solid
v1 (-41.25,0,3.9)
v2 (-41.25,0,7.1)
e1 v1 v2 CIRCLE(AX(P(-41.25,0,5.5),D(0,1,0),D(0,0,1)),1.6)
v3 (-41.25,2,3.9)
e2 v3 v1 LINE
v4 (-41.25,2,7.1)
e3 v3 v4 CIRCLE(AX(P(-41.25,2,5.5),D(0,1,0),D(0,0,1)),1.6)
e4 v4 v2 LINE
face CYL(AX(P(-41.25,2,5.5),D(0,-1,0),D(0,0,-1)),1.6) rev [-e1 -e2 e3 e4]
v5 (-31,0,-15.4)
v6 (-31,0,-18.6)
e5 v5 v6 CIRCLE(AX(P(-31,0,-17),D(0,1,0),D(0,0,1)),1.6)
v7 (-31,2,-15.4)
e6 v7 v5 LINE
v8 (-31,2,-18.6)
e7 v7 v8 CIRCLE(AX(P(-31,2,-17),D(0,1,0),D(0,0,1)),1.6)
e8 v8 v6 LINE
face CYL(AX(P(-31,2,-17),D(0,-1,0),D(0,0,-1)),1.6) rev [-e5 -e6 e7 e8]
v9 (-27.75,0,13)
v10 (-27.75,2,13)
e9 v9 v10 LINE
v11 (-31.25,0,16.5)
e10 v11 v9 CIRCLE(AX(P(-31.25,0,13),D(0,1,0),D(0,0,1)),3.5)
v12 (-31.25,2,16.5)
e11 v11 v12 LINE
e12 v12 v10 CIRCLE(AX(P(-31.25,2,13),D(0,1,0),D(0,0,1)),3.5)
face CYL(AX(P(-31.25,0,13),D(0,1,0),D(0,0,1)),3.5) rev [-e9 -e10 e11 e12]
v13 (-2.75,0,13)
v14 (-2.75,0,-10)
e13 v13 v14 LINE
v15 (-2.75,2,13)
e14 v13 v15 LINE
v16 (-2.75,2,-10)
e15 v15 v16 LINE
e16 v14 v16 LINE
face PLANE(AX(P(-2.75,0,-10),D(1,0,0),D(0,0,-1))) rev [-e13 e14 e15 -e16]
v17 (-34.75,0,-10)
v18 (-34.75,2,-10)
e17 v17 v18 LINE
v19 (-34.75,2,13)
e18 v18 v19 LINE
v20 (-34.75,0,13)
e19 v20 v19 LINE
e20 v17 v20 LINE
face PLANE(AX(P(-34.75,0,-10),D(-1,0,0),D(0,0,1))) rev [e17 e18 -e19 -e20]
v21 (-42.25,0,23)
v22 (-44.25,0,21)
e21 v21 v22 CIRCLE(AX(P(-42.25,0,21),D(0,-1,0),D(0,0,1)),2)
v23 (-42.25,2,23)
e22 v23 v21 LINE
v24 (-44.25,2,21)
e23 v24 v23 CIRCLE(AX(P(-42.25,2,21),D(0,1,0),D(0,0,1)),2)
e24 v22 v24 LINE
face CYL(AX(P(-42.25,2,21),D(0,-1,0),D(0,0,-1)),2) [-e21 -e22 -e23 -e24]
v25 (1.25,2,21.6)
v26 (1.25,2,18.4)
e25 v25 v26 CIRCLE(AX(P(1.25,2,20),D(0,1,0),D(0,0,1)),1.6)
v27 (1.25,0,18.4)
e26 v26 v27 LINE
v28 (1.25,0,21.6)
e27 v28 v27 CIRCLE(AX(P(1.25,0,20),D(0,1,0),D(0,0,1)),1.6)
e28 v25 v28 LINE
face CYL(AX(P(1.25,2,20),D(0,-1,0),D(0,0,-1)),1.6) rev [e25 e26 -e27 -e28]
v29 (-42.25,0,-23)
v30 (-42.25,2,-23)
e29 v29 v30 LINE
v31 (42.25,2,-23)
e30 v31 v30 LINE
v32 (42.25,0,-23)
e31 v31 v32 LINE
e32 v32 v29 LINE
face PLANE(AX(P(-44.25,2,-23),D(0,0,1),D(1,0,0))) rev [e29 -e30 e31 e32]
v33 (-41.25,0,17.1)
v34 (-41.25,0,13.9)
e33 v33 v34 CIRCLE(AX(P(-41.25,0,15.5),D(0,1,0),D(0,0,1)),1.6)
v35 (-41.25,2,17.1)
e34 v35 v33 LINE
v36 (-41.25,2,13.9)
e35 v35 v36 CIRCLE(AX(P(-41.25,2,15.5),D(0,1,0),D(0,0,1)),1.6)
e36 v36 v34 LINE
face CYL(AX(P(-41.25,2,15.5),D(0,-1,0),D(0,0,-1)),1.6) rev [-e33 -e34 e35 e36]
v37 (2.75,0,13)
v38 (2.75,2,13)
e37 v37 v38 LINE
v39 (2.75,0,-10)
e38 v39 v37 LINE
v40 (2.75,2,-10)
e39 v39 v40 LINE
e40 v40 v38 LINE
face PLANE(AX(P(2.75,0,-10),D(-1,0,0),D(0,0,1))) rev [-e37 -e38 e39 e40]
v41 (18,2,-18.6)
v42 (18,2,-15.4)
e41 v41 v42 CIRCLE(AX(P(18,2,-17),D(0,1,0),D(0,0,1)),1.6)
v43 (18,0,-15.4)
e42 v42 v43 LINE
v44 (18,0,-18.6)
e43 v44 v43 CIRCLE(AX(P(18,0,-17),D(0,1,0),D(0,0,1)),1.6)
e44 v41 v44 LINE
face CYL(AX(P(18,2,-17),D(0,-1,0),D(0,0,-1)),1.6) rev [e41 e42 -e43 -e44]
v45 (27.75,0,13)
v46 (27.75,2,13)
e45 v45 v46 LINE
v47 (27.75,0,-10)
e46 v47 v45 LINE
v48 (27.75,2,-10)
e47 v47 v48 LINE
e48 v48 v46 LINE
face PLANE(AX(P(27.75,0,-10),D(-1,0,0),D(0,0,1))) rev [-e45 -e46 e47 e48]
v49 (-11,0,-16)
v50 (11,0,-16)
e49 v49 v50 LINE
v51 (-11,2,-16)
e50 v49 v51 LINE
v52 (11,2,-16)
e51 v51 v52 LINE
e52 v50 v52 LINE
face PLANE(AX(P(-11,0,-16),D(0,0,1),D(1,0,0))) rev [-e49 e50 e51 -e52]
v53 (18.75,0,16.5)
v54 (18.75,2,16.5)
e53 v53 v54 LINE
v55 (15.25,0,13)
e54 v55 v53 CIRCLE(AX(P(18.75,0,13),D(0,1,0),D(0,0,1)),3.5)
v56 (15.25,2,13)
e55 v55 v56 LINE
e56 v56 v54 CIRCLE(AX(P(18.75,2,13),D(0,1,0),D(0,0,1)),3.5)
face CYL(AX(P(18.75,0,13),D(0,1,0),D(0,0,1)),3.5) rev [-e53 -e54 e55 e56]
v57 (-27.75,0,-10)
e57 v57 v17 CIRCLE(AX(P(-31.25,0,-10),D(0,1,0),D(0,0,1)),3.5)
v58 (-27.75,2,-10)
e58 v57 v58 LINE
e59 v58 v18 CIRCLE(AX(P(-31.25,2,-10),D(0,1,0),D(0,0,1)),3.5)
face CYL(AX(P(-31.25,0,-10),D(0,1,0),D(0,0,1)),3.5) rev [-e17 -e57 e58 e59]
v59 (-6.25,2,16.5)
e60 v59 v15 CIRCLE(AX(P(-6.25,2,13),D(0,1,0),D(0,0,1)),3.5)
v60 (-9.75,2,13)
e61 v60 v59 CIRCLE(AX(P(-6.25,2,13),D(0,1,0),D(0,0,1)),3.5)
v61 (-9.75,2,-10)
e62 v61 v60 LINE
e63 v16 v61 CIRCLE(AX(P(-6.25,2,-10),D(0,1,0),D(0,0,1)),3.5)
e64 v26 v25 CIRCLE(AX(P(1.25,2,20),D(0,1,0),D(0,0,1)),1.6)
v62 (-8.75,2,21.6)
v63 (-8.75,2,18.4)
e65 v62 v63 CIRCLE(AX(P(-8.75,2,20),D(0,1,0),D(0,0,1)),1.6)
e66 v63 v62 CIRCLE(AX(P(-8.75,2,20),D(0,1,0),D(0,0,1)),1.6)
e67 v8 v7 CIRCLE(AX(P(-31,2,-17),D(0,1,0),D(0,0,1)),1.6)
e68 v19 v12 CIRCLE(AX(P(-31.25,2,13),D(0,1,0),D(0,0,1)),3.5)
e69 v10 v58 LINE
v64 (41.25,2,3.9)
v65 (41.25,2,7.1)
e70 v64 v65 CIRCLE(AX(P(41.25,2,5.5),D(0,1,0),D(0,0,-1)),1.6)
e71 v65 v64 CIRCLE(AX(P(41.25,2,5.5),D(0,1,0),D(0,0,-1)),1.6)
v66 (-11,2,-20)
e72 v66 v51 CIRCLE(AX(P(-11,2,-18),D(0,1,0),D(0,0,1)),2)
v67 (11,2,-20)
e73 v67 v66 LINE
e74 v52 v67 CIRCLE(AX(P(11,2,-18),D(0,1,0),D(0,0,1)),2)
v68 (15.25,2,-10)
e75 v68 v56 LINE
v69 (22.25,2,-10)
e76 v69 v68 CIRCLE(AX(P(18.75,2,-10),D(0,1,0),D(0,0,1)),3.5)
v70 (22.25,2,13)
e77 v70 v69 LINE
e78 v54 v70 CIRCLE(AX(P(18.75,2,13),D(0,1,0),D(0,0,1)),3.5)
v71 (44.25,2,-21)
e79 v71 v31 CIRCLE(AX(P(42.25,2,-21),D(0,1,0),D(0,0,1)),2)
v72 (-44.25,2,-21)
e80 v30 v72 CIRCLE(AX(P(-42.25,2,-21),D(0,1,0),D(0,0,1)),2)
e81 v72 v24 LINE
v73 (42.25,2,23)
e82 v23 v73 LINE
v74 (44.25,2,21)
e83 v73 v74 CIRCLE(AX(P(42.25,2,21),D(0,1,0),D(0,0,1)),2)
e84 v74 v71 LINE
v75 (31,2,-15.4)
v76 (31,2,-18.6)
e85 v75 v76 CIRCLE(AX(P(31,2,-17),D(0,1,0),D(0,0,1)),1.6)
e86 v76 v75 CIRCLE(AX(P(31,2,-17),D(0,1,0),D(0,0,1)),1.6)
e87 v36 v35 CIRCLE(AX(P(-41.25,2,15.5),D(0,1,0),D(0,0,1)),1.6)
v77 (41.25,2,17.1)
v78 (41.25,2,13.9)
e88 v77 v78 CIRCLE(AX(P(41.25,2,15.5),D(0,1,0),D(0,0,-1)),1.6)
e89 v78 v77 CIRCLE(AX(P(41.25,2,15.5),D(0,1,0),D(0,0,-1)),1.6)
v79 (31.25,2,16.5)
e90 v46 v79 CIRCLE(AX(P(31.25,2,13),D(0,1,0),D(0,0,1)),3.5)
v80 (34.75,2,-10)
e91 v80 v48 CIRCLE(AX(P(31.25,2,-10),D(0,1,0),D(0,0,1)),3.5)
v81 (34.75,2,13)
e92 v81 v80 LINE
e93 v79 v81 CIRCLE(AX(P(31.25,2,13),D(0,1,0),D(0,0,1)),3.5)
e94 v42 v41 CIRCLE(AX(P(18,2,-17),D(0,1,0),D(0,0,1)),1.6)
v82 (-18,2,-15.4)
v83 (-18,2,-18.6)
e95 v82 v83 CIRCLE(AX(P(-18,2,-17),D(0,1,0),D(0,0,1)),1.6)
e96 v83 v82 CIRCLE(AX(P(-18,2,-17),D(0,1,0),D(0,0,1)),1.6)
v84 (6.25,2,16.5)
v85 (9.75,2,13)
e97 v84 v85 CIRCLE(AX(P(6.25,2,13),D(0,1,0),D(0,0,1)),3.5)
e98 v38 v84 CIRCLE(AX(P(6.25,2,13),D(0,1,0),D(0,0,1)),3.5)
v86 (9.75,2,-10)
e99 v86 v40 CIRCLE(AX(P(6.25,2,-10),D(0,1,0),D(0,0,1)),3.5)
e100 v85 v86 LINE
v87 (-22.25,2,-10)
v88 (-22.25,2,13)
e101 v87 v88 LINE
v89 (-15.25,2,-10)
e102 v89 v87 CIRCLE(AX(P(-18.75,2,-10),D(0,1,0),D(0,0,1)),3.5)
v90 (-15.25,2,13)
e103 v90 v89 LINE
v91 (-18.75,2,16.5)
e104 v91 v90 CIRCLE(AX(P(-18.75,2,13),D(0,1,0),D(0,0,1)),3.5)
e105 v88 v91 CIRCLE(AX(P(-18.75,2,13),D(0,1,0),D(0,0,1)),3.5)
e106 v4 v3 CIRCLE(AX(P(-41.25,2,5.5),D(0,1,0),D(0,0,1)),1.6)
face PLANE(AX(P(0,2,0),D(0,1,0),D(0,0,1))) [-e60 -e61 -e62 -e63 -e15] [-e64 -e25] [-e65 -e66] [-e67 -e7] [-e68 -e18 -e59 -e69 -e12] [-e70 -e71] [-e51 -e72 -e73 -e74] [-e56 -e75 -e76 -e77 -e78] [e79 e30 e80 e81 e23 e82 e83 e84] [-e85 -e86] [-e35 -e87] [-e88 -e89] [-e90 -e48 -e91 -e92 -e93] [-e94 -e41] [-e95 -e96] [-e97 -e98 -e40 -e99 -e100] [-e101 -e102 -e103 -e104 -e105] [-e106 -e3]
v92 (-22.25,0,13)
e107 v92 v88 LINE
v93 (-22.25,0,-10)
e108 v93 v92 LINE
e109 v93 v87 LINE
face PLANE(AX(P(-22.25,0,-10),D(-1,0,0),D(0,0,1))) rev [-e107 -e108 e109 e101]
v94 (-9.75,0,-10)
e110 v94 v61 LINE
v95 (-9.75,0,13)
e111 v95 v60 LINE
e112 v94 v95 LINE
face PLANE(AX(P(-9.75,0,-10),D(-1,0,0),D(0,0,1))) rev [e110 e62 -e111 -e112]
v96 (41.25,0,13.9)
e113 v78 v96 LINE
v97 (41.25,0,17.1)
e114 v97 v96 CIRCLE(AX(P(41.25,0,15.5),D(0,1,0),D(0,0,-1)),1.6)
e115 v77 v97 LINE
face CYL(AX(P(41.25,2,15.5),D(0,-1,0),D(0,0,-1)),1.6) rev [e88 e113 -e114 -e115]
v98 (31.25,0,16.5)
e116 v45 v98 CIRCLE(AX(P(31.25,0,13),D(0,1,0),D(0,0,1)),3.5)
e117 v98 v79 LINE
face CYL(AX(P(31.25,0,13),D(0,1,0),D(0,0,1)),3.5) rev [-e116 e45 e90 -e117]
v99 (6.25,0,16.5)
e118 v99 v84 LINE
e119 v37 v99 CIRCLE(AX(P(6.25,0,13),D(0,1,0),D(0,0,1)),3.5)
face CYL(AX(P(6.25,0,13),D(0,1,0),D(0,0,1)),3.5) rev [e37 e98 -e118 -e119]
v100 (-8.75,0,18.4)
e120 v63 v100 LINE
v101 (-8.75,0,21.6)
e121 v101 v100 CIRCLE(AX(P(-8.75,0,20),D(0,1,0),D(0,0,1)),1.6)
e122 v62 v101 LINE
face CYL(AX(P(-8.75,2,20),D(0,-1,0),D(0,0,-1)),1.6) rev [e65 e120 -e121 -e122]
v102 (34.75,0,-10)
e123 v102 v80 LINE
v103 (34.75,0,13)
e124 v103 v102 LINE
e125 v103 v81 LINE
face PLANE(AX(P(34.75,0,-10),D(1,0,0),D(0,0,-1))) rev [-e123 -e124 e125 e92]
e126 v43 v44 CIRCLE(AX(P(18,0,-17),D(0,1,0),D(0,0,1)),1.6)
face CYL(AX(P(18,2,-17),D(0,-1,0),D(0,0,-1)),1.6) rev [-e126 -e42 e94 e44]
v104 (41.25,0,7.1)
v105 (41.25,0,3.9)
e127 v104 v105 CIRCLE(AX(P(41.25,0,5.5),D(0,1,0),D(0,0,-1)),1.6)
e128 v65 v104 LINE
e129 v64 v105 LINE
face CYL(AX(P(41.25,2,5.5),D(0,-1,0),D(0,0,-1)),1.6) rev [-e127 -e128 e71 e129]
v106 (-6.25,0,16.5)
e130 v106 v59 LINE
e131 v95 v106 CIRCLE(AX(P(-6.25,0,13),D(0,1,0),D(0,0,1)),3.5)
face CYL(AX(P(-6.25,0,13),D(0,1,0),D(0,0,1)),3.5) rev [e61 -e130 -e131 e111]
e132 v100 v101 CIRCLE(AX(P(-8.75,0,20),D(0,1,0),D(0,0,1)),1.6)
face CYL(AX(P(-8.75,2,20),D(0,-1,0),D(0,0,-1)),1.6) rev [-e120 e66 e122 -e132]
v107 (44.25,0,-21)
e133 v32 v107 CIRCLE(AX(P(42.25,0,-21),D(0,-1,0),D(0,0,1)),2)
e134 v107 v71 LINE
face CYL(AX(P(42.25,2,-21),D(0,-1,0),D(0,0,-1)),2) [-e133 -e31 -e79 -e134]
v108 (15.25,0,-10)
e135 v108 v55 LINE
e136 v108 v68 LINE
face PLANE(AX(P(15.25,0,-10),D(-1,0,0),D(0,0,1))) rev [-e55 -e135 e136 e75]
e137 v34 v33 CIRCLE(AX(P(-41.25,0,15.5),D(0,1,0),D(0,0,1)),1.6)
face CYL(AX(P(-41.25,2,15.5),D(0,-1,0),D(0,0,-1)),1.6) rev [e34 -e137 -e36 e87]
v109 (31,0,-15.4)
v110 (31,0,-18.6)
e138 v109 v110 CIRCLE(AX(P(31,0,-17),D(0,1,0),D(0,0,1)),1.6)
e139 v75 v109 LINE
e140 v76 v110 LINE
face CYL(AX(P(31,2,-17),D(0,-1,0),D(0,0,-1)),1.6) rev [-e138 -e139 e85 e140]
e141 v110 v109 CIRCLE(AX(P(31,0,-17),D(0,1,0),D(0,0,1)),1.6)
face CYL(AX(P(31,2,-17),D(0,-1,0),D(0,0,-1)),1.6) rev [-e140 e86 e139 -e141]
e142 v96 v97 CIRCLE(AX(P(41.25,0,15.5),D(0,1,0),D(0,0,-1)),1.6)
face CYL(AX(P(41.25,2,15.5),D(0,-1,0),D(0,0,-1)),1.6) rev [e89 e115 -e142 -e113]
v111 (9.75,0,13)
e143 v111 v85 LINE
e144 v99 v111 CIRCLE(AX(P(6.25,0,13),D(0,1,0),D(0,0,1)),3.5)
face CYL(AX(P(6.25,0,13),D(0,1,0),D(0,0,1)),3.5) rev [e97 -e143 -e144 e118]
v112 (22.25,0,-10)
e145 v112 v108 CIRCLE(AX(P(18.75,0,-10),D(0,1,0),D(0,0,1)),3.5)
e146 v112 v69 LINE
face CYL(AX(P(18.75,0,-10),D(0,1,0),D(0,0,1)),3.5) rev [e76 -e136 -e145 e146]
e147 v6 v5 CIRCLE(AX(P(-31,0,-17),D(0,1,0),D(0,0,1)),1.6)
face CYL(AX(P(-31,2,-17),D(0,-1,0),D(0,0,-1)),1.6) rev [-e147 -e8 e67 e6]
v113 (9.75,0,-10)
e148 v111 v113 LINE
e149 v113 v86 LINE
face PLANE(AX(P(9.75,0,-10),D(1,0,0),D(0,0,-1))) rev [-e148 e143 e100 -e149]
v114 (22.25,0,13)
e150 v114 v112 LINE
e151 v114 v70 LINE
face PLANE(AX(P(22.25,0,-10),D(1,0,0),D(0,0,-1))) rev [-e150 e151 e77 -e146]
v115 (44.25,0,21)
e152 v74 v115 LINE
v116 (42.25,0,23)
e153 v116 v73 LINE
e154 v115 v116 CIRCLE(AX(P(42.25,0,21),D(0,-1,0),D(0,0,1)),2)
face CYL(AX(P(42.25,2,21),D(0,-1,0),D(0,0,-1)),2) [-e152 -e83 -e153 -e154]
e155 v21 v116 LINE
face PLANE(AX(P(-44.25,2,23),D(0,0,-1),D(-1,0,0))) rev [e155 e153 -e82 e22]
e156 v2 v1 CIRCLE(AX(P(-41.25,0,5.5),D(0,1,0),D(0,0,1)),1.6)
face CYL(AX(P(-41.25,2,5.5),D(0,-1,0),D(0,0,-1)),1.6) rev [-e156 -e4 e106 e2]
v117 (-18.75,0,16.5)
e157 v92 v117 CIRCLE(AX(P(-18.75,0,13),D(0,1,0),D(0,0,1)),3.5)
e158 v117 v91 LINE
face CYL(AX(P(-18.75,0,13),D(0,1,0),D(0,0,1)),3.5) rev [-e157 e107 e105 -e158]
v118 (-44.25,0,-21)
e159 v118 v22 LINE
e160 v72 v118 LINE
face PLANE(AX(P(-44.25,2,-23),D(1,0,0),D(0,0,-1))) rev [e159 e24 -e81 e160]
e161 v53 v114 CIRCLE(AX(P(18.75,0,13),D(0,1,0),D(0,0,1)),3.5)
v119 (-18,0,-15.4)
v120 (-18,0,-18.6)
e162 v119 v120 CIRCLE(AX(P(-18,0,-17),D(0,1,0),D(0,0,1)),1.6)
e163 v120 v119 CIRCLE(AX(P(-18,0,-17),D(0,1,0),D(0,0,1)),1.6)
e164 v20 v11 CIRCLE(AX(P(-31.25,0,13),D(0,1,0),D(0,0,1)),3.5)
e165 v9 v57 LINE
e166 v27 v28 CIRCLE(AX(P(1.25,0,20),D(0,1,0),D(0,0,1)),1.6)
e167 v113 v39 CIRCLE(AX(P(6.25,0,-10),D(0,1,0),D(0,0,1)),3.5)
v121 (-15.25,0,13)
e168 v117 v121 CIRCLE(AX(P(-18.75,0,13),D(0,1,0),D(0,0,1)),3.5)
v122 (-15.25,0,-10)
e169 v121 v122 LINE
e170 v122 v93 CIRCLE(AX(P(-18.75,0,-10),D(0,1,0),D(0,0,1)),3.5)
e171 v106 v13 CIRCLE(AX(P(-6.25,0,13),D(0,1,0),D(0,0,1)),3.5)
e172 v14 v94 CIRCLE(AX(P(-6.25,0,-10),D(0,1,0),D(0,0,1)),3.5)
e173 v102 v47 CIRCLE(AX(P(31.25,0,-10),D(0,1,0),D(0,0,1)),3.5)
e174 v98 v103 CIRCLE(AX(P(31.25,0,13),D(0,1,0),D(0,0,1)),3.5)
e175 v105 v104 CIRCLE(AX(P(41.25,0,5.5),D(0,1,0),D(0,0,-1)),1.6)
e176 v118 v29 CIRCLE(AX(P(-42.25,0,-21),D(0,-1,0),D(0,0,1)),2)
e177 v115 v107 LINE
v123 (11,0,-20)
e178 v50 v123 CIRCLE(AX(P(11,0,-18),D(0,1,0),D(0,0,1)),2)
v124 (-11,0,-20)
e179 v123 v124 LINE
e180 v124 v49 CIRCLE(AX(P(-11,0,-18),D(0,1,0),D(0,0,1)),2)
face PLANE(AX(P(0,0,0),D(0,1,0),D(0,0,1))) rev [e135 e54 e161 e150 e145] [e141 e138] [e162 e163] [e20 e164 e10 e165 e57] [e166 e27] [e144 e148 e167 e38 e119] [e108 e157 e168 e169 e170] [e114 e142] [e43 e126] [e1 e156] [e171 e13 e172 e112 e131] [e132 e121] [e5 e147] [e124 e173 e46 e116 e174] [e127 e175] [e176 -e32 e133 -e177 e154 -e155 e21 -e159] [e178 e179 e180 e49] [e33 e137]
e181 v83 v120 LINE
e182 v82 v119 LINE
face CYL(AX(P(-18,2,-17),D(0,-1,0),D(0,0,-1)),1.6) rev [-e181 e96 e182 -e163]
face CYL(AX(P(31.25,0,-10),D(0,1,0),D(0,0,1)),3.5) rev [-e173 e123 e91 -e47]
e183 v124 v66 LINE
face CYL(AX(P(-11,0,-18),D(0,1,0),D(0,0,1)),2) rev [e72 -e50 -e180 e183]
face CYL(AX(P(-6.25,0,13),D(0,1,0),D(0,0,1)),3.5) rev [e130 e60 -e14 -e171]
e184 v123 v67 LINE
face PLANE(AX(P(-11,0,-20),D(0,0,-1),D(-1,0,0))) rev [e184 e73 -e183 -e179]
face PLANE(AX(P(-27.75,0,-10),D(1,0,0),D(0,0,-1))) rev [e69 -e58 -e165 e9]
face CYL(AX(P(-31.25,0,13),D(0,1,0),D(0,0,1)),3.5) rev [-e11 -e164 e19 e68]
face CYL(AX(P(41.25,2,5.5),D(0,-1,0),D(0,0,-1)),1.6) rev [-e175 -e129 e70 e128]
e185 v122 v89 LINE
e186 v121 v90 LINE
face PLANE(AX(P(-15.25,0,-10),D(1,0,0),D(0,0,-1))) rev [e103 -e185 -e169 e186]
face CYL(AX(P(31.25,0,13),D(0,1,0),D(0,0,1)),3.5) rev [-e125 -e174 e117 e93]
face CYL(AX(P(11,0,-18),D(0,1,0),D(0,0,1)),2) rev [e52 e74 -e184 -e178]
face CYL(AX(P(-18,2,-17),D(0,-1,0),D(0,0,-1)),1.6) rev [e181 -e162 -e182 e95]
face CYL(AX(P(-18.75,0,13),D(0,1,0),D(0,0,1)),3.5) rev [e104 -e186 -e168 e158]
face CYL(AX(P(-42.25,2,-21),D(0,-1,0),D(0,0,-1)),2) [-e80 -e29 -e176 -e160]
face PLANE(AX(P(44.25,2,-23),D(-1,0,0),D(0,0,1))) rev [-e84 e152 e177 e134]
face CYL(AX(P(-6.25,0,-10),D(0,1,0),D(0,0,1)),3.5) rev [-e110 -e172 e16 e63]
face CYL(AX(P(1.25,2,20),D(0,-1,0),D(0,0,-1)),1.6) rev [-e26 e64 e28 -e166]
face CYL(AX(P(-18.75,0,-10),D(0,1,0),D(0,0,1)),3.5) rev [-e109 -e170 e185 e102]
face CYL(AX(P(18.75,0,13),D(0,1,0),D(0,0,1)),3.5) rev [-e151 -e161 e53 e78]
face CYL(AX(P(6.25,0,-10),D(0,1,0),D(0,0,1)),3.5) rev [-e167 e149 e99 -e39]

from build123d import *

# Parameters (mm, degrees)
SKETCH_1_W          = 88.5
SKETCH_1_H          = 46
SKETCH_1_R          = 1.6
EXTRUDE_1_DEPTH     = 2
CUT_EXTRUDE_1_DEPTH = 50.910544978
FILLET_1_R          = 2


with BuildPart() as part:
    # 草图1 → 凸台-拉伸1 (new body)
    with BuildSketch(Plane(origin=(0, 0, 0), x_dir=(1, 0, 0), z_dir=(0, 1, 0))):
        Rectangle(SKETCH_1_W, SKETCH_1_H)
        with Locations(Location((-41.25, -5.5, 0), (0, 0, 270))):
            Circle(SKETCH_1_R, mode=Mode.SUBTRACT)
        with Locations(Location((-41.25, -15.5, 0), (0, 0, 270))):
            Circle(SKETCH_1_R, mode=Mode.SUBTRACT)
        with Locations(Location((41.25, -15.5, 0), (0, 0, 90))):
            Circle(SKETCH_1_R, mode=Mode.SUBTRACT)
        with Locations(Location((41.25, -5.5, 0), (0, 0, 90))):
            Circle(SKETCH_1_R, mode=Mode.SUBTRACT)
        with Locations(Location((-8.75, -20, 0), (0, 0, 270))):
            Circle(SKETCH_1_R, mode=Mode.SUBTRACT)
        with Locations(Location((1.25, -20, 0), (0, 0, 270))):
            Circle(SKETCH_1_R, mode=Mode.SUBTRACT)
        with Locations(Location((-31, 17, 0), (0, 0, 270))):
            Circle(SKETCH_1_R, mode=Mode.SUBTRACT)
        with Locations(Location((-18, 17, 0), (0, 0, 270))):
            Circle(SKETCH_1_R, mode=Mode.SUBTRACT)
        with Locations(Location((18, 17, 0), (0, 0, 270))):
            Circle(SKETCH_1_R, mode=Mode.SUBTRACT)
        with Locations(Location((31, 17, 0), (0, 0, 270))):
            Circle(SKETCH_1_R, mode=Mode.SUBTRACT)
    extrude(amount=EXTRUDE_1_DEPTH)

    # 草图2 → 切除-拉伸1 (cut, through all)
    with BuildSketch(Plane(origin=(0, 2, 0), x_dir=(1, 0, 0), z_dir=(0, 1, 0))):
        with BuildLine():
            Line((-27.75, 10), (-27.75, -13))
            ThreePointArc((-27.75, -13), (-31.25, -16.5), (-34.75, -13))
            Line((-34.75, -13), (-34.75, 10))
            ThreePointArc((-34.75, 10), (-31.25, 13.5), (-27.75, 10))
        make_face()
        with BuildLine():
            Line((-15.25, 10), (-15.25, -13))
            ThreePointArc((-15.25, -13), (-18.75, -16.5), (-22.25, -13))
            Line((-22.25, -13), (-22.25, 10))
            ThreePointArc((-22.25, 10), (-18.75, 13.5), (-15.25, 10))
        make_face()
        with BuildLine():
            Line((-2.75, 10), (-2.75, -13))
            ThreePointArc((-2.75, -13), (-6.25, -16.5), (-9.75, -13))
            Line((-9.75, -13), (-9.75, 10))
            ThreePointArc((-9.75, 10), (-6.25, 13.5), (-2.75, 10))
        make_face()
        with BuildLine():
            Line((9.75, 10), (9.75, -13))
            ThreePointArc((9.75, -13), (6.25, -16.5), (2.75, -13))
            Line((2.75, -13), (2.75, 10))
            ThreePointArc((2.75, 10), (6.25, 13.5), (9.75, 10))
        make_face()
        with BuildLine():
            Line((22.25, 10), (22.25, -13))
            ThreePointArc((22.25, -13), (18.75, -16.5), (15.25, -13))
            Line((15.25, -13), (15.25, 10))
            ThreePointArc((15.25, 10), (18.75, 13.5), (22.25, 10))
        make_face()
        with BuildLine():
            Line((34.75, 10), (34.75, -13))
            ThreePointArc((34.75, -13), (31.25, -16.5), (27.75, -13))
            Line((27.75, -13), (27.75, 10))
            ThreePointArc((27.75, 10), (31.25, 13.5), (34.75, 10))
        make_face()
        with BuildLine():
            Line((-11, 20), (11, 20))
            ThreePointArc((11, 20), (13, 18), (11, 16))
            Line((11, 16), (-11, 16))
            ThreePointArc((-11, 16), (-13, 18), (-11, 20))
        make_face()
    extrude(amount=-CUT_EXTRUDE_1_DEPTH, mode=Mode.SUBTRACT)

    # 圆角1
    fillet_1_edges = [part.edges().sort_by_distance(p)[0] for p in [
        (44.25, 1, 23),
        (-44.25, 1, 23),
        (-44.25, 1, -23),
        (44.25, 1, -23),
    ]]
    fillet(fillet_1_edges, radius=FILLET_1_R)


solid = part.part
